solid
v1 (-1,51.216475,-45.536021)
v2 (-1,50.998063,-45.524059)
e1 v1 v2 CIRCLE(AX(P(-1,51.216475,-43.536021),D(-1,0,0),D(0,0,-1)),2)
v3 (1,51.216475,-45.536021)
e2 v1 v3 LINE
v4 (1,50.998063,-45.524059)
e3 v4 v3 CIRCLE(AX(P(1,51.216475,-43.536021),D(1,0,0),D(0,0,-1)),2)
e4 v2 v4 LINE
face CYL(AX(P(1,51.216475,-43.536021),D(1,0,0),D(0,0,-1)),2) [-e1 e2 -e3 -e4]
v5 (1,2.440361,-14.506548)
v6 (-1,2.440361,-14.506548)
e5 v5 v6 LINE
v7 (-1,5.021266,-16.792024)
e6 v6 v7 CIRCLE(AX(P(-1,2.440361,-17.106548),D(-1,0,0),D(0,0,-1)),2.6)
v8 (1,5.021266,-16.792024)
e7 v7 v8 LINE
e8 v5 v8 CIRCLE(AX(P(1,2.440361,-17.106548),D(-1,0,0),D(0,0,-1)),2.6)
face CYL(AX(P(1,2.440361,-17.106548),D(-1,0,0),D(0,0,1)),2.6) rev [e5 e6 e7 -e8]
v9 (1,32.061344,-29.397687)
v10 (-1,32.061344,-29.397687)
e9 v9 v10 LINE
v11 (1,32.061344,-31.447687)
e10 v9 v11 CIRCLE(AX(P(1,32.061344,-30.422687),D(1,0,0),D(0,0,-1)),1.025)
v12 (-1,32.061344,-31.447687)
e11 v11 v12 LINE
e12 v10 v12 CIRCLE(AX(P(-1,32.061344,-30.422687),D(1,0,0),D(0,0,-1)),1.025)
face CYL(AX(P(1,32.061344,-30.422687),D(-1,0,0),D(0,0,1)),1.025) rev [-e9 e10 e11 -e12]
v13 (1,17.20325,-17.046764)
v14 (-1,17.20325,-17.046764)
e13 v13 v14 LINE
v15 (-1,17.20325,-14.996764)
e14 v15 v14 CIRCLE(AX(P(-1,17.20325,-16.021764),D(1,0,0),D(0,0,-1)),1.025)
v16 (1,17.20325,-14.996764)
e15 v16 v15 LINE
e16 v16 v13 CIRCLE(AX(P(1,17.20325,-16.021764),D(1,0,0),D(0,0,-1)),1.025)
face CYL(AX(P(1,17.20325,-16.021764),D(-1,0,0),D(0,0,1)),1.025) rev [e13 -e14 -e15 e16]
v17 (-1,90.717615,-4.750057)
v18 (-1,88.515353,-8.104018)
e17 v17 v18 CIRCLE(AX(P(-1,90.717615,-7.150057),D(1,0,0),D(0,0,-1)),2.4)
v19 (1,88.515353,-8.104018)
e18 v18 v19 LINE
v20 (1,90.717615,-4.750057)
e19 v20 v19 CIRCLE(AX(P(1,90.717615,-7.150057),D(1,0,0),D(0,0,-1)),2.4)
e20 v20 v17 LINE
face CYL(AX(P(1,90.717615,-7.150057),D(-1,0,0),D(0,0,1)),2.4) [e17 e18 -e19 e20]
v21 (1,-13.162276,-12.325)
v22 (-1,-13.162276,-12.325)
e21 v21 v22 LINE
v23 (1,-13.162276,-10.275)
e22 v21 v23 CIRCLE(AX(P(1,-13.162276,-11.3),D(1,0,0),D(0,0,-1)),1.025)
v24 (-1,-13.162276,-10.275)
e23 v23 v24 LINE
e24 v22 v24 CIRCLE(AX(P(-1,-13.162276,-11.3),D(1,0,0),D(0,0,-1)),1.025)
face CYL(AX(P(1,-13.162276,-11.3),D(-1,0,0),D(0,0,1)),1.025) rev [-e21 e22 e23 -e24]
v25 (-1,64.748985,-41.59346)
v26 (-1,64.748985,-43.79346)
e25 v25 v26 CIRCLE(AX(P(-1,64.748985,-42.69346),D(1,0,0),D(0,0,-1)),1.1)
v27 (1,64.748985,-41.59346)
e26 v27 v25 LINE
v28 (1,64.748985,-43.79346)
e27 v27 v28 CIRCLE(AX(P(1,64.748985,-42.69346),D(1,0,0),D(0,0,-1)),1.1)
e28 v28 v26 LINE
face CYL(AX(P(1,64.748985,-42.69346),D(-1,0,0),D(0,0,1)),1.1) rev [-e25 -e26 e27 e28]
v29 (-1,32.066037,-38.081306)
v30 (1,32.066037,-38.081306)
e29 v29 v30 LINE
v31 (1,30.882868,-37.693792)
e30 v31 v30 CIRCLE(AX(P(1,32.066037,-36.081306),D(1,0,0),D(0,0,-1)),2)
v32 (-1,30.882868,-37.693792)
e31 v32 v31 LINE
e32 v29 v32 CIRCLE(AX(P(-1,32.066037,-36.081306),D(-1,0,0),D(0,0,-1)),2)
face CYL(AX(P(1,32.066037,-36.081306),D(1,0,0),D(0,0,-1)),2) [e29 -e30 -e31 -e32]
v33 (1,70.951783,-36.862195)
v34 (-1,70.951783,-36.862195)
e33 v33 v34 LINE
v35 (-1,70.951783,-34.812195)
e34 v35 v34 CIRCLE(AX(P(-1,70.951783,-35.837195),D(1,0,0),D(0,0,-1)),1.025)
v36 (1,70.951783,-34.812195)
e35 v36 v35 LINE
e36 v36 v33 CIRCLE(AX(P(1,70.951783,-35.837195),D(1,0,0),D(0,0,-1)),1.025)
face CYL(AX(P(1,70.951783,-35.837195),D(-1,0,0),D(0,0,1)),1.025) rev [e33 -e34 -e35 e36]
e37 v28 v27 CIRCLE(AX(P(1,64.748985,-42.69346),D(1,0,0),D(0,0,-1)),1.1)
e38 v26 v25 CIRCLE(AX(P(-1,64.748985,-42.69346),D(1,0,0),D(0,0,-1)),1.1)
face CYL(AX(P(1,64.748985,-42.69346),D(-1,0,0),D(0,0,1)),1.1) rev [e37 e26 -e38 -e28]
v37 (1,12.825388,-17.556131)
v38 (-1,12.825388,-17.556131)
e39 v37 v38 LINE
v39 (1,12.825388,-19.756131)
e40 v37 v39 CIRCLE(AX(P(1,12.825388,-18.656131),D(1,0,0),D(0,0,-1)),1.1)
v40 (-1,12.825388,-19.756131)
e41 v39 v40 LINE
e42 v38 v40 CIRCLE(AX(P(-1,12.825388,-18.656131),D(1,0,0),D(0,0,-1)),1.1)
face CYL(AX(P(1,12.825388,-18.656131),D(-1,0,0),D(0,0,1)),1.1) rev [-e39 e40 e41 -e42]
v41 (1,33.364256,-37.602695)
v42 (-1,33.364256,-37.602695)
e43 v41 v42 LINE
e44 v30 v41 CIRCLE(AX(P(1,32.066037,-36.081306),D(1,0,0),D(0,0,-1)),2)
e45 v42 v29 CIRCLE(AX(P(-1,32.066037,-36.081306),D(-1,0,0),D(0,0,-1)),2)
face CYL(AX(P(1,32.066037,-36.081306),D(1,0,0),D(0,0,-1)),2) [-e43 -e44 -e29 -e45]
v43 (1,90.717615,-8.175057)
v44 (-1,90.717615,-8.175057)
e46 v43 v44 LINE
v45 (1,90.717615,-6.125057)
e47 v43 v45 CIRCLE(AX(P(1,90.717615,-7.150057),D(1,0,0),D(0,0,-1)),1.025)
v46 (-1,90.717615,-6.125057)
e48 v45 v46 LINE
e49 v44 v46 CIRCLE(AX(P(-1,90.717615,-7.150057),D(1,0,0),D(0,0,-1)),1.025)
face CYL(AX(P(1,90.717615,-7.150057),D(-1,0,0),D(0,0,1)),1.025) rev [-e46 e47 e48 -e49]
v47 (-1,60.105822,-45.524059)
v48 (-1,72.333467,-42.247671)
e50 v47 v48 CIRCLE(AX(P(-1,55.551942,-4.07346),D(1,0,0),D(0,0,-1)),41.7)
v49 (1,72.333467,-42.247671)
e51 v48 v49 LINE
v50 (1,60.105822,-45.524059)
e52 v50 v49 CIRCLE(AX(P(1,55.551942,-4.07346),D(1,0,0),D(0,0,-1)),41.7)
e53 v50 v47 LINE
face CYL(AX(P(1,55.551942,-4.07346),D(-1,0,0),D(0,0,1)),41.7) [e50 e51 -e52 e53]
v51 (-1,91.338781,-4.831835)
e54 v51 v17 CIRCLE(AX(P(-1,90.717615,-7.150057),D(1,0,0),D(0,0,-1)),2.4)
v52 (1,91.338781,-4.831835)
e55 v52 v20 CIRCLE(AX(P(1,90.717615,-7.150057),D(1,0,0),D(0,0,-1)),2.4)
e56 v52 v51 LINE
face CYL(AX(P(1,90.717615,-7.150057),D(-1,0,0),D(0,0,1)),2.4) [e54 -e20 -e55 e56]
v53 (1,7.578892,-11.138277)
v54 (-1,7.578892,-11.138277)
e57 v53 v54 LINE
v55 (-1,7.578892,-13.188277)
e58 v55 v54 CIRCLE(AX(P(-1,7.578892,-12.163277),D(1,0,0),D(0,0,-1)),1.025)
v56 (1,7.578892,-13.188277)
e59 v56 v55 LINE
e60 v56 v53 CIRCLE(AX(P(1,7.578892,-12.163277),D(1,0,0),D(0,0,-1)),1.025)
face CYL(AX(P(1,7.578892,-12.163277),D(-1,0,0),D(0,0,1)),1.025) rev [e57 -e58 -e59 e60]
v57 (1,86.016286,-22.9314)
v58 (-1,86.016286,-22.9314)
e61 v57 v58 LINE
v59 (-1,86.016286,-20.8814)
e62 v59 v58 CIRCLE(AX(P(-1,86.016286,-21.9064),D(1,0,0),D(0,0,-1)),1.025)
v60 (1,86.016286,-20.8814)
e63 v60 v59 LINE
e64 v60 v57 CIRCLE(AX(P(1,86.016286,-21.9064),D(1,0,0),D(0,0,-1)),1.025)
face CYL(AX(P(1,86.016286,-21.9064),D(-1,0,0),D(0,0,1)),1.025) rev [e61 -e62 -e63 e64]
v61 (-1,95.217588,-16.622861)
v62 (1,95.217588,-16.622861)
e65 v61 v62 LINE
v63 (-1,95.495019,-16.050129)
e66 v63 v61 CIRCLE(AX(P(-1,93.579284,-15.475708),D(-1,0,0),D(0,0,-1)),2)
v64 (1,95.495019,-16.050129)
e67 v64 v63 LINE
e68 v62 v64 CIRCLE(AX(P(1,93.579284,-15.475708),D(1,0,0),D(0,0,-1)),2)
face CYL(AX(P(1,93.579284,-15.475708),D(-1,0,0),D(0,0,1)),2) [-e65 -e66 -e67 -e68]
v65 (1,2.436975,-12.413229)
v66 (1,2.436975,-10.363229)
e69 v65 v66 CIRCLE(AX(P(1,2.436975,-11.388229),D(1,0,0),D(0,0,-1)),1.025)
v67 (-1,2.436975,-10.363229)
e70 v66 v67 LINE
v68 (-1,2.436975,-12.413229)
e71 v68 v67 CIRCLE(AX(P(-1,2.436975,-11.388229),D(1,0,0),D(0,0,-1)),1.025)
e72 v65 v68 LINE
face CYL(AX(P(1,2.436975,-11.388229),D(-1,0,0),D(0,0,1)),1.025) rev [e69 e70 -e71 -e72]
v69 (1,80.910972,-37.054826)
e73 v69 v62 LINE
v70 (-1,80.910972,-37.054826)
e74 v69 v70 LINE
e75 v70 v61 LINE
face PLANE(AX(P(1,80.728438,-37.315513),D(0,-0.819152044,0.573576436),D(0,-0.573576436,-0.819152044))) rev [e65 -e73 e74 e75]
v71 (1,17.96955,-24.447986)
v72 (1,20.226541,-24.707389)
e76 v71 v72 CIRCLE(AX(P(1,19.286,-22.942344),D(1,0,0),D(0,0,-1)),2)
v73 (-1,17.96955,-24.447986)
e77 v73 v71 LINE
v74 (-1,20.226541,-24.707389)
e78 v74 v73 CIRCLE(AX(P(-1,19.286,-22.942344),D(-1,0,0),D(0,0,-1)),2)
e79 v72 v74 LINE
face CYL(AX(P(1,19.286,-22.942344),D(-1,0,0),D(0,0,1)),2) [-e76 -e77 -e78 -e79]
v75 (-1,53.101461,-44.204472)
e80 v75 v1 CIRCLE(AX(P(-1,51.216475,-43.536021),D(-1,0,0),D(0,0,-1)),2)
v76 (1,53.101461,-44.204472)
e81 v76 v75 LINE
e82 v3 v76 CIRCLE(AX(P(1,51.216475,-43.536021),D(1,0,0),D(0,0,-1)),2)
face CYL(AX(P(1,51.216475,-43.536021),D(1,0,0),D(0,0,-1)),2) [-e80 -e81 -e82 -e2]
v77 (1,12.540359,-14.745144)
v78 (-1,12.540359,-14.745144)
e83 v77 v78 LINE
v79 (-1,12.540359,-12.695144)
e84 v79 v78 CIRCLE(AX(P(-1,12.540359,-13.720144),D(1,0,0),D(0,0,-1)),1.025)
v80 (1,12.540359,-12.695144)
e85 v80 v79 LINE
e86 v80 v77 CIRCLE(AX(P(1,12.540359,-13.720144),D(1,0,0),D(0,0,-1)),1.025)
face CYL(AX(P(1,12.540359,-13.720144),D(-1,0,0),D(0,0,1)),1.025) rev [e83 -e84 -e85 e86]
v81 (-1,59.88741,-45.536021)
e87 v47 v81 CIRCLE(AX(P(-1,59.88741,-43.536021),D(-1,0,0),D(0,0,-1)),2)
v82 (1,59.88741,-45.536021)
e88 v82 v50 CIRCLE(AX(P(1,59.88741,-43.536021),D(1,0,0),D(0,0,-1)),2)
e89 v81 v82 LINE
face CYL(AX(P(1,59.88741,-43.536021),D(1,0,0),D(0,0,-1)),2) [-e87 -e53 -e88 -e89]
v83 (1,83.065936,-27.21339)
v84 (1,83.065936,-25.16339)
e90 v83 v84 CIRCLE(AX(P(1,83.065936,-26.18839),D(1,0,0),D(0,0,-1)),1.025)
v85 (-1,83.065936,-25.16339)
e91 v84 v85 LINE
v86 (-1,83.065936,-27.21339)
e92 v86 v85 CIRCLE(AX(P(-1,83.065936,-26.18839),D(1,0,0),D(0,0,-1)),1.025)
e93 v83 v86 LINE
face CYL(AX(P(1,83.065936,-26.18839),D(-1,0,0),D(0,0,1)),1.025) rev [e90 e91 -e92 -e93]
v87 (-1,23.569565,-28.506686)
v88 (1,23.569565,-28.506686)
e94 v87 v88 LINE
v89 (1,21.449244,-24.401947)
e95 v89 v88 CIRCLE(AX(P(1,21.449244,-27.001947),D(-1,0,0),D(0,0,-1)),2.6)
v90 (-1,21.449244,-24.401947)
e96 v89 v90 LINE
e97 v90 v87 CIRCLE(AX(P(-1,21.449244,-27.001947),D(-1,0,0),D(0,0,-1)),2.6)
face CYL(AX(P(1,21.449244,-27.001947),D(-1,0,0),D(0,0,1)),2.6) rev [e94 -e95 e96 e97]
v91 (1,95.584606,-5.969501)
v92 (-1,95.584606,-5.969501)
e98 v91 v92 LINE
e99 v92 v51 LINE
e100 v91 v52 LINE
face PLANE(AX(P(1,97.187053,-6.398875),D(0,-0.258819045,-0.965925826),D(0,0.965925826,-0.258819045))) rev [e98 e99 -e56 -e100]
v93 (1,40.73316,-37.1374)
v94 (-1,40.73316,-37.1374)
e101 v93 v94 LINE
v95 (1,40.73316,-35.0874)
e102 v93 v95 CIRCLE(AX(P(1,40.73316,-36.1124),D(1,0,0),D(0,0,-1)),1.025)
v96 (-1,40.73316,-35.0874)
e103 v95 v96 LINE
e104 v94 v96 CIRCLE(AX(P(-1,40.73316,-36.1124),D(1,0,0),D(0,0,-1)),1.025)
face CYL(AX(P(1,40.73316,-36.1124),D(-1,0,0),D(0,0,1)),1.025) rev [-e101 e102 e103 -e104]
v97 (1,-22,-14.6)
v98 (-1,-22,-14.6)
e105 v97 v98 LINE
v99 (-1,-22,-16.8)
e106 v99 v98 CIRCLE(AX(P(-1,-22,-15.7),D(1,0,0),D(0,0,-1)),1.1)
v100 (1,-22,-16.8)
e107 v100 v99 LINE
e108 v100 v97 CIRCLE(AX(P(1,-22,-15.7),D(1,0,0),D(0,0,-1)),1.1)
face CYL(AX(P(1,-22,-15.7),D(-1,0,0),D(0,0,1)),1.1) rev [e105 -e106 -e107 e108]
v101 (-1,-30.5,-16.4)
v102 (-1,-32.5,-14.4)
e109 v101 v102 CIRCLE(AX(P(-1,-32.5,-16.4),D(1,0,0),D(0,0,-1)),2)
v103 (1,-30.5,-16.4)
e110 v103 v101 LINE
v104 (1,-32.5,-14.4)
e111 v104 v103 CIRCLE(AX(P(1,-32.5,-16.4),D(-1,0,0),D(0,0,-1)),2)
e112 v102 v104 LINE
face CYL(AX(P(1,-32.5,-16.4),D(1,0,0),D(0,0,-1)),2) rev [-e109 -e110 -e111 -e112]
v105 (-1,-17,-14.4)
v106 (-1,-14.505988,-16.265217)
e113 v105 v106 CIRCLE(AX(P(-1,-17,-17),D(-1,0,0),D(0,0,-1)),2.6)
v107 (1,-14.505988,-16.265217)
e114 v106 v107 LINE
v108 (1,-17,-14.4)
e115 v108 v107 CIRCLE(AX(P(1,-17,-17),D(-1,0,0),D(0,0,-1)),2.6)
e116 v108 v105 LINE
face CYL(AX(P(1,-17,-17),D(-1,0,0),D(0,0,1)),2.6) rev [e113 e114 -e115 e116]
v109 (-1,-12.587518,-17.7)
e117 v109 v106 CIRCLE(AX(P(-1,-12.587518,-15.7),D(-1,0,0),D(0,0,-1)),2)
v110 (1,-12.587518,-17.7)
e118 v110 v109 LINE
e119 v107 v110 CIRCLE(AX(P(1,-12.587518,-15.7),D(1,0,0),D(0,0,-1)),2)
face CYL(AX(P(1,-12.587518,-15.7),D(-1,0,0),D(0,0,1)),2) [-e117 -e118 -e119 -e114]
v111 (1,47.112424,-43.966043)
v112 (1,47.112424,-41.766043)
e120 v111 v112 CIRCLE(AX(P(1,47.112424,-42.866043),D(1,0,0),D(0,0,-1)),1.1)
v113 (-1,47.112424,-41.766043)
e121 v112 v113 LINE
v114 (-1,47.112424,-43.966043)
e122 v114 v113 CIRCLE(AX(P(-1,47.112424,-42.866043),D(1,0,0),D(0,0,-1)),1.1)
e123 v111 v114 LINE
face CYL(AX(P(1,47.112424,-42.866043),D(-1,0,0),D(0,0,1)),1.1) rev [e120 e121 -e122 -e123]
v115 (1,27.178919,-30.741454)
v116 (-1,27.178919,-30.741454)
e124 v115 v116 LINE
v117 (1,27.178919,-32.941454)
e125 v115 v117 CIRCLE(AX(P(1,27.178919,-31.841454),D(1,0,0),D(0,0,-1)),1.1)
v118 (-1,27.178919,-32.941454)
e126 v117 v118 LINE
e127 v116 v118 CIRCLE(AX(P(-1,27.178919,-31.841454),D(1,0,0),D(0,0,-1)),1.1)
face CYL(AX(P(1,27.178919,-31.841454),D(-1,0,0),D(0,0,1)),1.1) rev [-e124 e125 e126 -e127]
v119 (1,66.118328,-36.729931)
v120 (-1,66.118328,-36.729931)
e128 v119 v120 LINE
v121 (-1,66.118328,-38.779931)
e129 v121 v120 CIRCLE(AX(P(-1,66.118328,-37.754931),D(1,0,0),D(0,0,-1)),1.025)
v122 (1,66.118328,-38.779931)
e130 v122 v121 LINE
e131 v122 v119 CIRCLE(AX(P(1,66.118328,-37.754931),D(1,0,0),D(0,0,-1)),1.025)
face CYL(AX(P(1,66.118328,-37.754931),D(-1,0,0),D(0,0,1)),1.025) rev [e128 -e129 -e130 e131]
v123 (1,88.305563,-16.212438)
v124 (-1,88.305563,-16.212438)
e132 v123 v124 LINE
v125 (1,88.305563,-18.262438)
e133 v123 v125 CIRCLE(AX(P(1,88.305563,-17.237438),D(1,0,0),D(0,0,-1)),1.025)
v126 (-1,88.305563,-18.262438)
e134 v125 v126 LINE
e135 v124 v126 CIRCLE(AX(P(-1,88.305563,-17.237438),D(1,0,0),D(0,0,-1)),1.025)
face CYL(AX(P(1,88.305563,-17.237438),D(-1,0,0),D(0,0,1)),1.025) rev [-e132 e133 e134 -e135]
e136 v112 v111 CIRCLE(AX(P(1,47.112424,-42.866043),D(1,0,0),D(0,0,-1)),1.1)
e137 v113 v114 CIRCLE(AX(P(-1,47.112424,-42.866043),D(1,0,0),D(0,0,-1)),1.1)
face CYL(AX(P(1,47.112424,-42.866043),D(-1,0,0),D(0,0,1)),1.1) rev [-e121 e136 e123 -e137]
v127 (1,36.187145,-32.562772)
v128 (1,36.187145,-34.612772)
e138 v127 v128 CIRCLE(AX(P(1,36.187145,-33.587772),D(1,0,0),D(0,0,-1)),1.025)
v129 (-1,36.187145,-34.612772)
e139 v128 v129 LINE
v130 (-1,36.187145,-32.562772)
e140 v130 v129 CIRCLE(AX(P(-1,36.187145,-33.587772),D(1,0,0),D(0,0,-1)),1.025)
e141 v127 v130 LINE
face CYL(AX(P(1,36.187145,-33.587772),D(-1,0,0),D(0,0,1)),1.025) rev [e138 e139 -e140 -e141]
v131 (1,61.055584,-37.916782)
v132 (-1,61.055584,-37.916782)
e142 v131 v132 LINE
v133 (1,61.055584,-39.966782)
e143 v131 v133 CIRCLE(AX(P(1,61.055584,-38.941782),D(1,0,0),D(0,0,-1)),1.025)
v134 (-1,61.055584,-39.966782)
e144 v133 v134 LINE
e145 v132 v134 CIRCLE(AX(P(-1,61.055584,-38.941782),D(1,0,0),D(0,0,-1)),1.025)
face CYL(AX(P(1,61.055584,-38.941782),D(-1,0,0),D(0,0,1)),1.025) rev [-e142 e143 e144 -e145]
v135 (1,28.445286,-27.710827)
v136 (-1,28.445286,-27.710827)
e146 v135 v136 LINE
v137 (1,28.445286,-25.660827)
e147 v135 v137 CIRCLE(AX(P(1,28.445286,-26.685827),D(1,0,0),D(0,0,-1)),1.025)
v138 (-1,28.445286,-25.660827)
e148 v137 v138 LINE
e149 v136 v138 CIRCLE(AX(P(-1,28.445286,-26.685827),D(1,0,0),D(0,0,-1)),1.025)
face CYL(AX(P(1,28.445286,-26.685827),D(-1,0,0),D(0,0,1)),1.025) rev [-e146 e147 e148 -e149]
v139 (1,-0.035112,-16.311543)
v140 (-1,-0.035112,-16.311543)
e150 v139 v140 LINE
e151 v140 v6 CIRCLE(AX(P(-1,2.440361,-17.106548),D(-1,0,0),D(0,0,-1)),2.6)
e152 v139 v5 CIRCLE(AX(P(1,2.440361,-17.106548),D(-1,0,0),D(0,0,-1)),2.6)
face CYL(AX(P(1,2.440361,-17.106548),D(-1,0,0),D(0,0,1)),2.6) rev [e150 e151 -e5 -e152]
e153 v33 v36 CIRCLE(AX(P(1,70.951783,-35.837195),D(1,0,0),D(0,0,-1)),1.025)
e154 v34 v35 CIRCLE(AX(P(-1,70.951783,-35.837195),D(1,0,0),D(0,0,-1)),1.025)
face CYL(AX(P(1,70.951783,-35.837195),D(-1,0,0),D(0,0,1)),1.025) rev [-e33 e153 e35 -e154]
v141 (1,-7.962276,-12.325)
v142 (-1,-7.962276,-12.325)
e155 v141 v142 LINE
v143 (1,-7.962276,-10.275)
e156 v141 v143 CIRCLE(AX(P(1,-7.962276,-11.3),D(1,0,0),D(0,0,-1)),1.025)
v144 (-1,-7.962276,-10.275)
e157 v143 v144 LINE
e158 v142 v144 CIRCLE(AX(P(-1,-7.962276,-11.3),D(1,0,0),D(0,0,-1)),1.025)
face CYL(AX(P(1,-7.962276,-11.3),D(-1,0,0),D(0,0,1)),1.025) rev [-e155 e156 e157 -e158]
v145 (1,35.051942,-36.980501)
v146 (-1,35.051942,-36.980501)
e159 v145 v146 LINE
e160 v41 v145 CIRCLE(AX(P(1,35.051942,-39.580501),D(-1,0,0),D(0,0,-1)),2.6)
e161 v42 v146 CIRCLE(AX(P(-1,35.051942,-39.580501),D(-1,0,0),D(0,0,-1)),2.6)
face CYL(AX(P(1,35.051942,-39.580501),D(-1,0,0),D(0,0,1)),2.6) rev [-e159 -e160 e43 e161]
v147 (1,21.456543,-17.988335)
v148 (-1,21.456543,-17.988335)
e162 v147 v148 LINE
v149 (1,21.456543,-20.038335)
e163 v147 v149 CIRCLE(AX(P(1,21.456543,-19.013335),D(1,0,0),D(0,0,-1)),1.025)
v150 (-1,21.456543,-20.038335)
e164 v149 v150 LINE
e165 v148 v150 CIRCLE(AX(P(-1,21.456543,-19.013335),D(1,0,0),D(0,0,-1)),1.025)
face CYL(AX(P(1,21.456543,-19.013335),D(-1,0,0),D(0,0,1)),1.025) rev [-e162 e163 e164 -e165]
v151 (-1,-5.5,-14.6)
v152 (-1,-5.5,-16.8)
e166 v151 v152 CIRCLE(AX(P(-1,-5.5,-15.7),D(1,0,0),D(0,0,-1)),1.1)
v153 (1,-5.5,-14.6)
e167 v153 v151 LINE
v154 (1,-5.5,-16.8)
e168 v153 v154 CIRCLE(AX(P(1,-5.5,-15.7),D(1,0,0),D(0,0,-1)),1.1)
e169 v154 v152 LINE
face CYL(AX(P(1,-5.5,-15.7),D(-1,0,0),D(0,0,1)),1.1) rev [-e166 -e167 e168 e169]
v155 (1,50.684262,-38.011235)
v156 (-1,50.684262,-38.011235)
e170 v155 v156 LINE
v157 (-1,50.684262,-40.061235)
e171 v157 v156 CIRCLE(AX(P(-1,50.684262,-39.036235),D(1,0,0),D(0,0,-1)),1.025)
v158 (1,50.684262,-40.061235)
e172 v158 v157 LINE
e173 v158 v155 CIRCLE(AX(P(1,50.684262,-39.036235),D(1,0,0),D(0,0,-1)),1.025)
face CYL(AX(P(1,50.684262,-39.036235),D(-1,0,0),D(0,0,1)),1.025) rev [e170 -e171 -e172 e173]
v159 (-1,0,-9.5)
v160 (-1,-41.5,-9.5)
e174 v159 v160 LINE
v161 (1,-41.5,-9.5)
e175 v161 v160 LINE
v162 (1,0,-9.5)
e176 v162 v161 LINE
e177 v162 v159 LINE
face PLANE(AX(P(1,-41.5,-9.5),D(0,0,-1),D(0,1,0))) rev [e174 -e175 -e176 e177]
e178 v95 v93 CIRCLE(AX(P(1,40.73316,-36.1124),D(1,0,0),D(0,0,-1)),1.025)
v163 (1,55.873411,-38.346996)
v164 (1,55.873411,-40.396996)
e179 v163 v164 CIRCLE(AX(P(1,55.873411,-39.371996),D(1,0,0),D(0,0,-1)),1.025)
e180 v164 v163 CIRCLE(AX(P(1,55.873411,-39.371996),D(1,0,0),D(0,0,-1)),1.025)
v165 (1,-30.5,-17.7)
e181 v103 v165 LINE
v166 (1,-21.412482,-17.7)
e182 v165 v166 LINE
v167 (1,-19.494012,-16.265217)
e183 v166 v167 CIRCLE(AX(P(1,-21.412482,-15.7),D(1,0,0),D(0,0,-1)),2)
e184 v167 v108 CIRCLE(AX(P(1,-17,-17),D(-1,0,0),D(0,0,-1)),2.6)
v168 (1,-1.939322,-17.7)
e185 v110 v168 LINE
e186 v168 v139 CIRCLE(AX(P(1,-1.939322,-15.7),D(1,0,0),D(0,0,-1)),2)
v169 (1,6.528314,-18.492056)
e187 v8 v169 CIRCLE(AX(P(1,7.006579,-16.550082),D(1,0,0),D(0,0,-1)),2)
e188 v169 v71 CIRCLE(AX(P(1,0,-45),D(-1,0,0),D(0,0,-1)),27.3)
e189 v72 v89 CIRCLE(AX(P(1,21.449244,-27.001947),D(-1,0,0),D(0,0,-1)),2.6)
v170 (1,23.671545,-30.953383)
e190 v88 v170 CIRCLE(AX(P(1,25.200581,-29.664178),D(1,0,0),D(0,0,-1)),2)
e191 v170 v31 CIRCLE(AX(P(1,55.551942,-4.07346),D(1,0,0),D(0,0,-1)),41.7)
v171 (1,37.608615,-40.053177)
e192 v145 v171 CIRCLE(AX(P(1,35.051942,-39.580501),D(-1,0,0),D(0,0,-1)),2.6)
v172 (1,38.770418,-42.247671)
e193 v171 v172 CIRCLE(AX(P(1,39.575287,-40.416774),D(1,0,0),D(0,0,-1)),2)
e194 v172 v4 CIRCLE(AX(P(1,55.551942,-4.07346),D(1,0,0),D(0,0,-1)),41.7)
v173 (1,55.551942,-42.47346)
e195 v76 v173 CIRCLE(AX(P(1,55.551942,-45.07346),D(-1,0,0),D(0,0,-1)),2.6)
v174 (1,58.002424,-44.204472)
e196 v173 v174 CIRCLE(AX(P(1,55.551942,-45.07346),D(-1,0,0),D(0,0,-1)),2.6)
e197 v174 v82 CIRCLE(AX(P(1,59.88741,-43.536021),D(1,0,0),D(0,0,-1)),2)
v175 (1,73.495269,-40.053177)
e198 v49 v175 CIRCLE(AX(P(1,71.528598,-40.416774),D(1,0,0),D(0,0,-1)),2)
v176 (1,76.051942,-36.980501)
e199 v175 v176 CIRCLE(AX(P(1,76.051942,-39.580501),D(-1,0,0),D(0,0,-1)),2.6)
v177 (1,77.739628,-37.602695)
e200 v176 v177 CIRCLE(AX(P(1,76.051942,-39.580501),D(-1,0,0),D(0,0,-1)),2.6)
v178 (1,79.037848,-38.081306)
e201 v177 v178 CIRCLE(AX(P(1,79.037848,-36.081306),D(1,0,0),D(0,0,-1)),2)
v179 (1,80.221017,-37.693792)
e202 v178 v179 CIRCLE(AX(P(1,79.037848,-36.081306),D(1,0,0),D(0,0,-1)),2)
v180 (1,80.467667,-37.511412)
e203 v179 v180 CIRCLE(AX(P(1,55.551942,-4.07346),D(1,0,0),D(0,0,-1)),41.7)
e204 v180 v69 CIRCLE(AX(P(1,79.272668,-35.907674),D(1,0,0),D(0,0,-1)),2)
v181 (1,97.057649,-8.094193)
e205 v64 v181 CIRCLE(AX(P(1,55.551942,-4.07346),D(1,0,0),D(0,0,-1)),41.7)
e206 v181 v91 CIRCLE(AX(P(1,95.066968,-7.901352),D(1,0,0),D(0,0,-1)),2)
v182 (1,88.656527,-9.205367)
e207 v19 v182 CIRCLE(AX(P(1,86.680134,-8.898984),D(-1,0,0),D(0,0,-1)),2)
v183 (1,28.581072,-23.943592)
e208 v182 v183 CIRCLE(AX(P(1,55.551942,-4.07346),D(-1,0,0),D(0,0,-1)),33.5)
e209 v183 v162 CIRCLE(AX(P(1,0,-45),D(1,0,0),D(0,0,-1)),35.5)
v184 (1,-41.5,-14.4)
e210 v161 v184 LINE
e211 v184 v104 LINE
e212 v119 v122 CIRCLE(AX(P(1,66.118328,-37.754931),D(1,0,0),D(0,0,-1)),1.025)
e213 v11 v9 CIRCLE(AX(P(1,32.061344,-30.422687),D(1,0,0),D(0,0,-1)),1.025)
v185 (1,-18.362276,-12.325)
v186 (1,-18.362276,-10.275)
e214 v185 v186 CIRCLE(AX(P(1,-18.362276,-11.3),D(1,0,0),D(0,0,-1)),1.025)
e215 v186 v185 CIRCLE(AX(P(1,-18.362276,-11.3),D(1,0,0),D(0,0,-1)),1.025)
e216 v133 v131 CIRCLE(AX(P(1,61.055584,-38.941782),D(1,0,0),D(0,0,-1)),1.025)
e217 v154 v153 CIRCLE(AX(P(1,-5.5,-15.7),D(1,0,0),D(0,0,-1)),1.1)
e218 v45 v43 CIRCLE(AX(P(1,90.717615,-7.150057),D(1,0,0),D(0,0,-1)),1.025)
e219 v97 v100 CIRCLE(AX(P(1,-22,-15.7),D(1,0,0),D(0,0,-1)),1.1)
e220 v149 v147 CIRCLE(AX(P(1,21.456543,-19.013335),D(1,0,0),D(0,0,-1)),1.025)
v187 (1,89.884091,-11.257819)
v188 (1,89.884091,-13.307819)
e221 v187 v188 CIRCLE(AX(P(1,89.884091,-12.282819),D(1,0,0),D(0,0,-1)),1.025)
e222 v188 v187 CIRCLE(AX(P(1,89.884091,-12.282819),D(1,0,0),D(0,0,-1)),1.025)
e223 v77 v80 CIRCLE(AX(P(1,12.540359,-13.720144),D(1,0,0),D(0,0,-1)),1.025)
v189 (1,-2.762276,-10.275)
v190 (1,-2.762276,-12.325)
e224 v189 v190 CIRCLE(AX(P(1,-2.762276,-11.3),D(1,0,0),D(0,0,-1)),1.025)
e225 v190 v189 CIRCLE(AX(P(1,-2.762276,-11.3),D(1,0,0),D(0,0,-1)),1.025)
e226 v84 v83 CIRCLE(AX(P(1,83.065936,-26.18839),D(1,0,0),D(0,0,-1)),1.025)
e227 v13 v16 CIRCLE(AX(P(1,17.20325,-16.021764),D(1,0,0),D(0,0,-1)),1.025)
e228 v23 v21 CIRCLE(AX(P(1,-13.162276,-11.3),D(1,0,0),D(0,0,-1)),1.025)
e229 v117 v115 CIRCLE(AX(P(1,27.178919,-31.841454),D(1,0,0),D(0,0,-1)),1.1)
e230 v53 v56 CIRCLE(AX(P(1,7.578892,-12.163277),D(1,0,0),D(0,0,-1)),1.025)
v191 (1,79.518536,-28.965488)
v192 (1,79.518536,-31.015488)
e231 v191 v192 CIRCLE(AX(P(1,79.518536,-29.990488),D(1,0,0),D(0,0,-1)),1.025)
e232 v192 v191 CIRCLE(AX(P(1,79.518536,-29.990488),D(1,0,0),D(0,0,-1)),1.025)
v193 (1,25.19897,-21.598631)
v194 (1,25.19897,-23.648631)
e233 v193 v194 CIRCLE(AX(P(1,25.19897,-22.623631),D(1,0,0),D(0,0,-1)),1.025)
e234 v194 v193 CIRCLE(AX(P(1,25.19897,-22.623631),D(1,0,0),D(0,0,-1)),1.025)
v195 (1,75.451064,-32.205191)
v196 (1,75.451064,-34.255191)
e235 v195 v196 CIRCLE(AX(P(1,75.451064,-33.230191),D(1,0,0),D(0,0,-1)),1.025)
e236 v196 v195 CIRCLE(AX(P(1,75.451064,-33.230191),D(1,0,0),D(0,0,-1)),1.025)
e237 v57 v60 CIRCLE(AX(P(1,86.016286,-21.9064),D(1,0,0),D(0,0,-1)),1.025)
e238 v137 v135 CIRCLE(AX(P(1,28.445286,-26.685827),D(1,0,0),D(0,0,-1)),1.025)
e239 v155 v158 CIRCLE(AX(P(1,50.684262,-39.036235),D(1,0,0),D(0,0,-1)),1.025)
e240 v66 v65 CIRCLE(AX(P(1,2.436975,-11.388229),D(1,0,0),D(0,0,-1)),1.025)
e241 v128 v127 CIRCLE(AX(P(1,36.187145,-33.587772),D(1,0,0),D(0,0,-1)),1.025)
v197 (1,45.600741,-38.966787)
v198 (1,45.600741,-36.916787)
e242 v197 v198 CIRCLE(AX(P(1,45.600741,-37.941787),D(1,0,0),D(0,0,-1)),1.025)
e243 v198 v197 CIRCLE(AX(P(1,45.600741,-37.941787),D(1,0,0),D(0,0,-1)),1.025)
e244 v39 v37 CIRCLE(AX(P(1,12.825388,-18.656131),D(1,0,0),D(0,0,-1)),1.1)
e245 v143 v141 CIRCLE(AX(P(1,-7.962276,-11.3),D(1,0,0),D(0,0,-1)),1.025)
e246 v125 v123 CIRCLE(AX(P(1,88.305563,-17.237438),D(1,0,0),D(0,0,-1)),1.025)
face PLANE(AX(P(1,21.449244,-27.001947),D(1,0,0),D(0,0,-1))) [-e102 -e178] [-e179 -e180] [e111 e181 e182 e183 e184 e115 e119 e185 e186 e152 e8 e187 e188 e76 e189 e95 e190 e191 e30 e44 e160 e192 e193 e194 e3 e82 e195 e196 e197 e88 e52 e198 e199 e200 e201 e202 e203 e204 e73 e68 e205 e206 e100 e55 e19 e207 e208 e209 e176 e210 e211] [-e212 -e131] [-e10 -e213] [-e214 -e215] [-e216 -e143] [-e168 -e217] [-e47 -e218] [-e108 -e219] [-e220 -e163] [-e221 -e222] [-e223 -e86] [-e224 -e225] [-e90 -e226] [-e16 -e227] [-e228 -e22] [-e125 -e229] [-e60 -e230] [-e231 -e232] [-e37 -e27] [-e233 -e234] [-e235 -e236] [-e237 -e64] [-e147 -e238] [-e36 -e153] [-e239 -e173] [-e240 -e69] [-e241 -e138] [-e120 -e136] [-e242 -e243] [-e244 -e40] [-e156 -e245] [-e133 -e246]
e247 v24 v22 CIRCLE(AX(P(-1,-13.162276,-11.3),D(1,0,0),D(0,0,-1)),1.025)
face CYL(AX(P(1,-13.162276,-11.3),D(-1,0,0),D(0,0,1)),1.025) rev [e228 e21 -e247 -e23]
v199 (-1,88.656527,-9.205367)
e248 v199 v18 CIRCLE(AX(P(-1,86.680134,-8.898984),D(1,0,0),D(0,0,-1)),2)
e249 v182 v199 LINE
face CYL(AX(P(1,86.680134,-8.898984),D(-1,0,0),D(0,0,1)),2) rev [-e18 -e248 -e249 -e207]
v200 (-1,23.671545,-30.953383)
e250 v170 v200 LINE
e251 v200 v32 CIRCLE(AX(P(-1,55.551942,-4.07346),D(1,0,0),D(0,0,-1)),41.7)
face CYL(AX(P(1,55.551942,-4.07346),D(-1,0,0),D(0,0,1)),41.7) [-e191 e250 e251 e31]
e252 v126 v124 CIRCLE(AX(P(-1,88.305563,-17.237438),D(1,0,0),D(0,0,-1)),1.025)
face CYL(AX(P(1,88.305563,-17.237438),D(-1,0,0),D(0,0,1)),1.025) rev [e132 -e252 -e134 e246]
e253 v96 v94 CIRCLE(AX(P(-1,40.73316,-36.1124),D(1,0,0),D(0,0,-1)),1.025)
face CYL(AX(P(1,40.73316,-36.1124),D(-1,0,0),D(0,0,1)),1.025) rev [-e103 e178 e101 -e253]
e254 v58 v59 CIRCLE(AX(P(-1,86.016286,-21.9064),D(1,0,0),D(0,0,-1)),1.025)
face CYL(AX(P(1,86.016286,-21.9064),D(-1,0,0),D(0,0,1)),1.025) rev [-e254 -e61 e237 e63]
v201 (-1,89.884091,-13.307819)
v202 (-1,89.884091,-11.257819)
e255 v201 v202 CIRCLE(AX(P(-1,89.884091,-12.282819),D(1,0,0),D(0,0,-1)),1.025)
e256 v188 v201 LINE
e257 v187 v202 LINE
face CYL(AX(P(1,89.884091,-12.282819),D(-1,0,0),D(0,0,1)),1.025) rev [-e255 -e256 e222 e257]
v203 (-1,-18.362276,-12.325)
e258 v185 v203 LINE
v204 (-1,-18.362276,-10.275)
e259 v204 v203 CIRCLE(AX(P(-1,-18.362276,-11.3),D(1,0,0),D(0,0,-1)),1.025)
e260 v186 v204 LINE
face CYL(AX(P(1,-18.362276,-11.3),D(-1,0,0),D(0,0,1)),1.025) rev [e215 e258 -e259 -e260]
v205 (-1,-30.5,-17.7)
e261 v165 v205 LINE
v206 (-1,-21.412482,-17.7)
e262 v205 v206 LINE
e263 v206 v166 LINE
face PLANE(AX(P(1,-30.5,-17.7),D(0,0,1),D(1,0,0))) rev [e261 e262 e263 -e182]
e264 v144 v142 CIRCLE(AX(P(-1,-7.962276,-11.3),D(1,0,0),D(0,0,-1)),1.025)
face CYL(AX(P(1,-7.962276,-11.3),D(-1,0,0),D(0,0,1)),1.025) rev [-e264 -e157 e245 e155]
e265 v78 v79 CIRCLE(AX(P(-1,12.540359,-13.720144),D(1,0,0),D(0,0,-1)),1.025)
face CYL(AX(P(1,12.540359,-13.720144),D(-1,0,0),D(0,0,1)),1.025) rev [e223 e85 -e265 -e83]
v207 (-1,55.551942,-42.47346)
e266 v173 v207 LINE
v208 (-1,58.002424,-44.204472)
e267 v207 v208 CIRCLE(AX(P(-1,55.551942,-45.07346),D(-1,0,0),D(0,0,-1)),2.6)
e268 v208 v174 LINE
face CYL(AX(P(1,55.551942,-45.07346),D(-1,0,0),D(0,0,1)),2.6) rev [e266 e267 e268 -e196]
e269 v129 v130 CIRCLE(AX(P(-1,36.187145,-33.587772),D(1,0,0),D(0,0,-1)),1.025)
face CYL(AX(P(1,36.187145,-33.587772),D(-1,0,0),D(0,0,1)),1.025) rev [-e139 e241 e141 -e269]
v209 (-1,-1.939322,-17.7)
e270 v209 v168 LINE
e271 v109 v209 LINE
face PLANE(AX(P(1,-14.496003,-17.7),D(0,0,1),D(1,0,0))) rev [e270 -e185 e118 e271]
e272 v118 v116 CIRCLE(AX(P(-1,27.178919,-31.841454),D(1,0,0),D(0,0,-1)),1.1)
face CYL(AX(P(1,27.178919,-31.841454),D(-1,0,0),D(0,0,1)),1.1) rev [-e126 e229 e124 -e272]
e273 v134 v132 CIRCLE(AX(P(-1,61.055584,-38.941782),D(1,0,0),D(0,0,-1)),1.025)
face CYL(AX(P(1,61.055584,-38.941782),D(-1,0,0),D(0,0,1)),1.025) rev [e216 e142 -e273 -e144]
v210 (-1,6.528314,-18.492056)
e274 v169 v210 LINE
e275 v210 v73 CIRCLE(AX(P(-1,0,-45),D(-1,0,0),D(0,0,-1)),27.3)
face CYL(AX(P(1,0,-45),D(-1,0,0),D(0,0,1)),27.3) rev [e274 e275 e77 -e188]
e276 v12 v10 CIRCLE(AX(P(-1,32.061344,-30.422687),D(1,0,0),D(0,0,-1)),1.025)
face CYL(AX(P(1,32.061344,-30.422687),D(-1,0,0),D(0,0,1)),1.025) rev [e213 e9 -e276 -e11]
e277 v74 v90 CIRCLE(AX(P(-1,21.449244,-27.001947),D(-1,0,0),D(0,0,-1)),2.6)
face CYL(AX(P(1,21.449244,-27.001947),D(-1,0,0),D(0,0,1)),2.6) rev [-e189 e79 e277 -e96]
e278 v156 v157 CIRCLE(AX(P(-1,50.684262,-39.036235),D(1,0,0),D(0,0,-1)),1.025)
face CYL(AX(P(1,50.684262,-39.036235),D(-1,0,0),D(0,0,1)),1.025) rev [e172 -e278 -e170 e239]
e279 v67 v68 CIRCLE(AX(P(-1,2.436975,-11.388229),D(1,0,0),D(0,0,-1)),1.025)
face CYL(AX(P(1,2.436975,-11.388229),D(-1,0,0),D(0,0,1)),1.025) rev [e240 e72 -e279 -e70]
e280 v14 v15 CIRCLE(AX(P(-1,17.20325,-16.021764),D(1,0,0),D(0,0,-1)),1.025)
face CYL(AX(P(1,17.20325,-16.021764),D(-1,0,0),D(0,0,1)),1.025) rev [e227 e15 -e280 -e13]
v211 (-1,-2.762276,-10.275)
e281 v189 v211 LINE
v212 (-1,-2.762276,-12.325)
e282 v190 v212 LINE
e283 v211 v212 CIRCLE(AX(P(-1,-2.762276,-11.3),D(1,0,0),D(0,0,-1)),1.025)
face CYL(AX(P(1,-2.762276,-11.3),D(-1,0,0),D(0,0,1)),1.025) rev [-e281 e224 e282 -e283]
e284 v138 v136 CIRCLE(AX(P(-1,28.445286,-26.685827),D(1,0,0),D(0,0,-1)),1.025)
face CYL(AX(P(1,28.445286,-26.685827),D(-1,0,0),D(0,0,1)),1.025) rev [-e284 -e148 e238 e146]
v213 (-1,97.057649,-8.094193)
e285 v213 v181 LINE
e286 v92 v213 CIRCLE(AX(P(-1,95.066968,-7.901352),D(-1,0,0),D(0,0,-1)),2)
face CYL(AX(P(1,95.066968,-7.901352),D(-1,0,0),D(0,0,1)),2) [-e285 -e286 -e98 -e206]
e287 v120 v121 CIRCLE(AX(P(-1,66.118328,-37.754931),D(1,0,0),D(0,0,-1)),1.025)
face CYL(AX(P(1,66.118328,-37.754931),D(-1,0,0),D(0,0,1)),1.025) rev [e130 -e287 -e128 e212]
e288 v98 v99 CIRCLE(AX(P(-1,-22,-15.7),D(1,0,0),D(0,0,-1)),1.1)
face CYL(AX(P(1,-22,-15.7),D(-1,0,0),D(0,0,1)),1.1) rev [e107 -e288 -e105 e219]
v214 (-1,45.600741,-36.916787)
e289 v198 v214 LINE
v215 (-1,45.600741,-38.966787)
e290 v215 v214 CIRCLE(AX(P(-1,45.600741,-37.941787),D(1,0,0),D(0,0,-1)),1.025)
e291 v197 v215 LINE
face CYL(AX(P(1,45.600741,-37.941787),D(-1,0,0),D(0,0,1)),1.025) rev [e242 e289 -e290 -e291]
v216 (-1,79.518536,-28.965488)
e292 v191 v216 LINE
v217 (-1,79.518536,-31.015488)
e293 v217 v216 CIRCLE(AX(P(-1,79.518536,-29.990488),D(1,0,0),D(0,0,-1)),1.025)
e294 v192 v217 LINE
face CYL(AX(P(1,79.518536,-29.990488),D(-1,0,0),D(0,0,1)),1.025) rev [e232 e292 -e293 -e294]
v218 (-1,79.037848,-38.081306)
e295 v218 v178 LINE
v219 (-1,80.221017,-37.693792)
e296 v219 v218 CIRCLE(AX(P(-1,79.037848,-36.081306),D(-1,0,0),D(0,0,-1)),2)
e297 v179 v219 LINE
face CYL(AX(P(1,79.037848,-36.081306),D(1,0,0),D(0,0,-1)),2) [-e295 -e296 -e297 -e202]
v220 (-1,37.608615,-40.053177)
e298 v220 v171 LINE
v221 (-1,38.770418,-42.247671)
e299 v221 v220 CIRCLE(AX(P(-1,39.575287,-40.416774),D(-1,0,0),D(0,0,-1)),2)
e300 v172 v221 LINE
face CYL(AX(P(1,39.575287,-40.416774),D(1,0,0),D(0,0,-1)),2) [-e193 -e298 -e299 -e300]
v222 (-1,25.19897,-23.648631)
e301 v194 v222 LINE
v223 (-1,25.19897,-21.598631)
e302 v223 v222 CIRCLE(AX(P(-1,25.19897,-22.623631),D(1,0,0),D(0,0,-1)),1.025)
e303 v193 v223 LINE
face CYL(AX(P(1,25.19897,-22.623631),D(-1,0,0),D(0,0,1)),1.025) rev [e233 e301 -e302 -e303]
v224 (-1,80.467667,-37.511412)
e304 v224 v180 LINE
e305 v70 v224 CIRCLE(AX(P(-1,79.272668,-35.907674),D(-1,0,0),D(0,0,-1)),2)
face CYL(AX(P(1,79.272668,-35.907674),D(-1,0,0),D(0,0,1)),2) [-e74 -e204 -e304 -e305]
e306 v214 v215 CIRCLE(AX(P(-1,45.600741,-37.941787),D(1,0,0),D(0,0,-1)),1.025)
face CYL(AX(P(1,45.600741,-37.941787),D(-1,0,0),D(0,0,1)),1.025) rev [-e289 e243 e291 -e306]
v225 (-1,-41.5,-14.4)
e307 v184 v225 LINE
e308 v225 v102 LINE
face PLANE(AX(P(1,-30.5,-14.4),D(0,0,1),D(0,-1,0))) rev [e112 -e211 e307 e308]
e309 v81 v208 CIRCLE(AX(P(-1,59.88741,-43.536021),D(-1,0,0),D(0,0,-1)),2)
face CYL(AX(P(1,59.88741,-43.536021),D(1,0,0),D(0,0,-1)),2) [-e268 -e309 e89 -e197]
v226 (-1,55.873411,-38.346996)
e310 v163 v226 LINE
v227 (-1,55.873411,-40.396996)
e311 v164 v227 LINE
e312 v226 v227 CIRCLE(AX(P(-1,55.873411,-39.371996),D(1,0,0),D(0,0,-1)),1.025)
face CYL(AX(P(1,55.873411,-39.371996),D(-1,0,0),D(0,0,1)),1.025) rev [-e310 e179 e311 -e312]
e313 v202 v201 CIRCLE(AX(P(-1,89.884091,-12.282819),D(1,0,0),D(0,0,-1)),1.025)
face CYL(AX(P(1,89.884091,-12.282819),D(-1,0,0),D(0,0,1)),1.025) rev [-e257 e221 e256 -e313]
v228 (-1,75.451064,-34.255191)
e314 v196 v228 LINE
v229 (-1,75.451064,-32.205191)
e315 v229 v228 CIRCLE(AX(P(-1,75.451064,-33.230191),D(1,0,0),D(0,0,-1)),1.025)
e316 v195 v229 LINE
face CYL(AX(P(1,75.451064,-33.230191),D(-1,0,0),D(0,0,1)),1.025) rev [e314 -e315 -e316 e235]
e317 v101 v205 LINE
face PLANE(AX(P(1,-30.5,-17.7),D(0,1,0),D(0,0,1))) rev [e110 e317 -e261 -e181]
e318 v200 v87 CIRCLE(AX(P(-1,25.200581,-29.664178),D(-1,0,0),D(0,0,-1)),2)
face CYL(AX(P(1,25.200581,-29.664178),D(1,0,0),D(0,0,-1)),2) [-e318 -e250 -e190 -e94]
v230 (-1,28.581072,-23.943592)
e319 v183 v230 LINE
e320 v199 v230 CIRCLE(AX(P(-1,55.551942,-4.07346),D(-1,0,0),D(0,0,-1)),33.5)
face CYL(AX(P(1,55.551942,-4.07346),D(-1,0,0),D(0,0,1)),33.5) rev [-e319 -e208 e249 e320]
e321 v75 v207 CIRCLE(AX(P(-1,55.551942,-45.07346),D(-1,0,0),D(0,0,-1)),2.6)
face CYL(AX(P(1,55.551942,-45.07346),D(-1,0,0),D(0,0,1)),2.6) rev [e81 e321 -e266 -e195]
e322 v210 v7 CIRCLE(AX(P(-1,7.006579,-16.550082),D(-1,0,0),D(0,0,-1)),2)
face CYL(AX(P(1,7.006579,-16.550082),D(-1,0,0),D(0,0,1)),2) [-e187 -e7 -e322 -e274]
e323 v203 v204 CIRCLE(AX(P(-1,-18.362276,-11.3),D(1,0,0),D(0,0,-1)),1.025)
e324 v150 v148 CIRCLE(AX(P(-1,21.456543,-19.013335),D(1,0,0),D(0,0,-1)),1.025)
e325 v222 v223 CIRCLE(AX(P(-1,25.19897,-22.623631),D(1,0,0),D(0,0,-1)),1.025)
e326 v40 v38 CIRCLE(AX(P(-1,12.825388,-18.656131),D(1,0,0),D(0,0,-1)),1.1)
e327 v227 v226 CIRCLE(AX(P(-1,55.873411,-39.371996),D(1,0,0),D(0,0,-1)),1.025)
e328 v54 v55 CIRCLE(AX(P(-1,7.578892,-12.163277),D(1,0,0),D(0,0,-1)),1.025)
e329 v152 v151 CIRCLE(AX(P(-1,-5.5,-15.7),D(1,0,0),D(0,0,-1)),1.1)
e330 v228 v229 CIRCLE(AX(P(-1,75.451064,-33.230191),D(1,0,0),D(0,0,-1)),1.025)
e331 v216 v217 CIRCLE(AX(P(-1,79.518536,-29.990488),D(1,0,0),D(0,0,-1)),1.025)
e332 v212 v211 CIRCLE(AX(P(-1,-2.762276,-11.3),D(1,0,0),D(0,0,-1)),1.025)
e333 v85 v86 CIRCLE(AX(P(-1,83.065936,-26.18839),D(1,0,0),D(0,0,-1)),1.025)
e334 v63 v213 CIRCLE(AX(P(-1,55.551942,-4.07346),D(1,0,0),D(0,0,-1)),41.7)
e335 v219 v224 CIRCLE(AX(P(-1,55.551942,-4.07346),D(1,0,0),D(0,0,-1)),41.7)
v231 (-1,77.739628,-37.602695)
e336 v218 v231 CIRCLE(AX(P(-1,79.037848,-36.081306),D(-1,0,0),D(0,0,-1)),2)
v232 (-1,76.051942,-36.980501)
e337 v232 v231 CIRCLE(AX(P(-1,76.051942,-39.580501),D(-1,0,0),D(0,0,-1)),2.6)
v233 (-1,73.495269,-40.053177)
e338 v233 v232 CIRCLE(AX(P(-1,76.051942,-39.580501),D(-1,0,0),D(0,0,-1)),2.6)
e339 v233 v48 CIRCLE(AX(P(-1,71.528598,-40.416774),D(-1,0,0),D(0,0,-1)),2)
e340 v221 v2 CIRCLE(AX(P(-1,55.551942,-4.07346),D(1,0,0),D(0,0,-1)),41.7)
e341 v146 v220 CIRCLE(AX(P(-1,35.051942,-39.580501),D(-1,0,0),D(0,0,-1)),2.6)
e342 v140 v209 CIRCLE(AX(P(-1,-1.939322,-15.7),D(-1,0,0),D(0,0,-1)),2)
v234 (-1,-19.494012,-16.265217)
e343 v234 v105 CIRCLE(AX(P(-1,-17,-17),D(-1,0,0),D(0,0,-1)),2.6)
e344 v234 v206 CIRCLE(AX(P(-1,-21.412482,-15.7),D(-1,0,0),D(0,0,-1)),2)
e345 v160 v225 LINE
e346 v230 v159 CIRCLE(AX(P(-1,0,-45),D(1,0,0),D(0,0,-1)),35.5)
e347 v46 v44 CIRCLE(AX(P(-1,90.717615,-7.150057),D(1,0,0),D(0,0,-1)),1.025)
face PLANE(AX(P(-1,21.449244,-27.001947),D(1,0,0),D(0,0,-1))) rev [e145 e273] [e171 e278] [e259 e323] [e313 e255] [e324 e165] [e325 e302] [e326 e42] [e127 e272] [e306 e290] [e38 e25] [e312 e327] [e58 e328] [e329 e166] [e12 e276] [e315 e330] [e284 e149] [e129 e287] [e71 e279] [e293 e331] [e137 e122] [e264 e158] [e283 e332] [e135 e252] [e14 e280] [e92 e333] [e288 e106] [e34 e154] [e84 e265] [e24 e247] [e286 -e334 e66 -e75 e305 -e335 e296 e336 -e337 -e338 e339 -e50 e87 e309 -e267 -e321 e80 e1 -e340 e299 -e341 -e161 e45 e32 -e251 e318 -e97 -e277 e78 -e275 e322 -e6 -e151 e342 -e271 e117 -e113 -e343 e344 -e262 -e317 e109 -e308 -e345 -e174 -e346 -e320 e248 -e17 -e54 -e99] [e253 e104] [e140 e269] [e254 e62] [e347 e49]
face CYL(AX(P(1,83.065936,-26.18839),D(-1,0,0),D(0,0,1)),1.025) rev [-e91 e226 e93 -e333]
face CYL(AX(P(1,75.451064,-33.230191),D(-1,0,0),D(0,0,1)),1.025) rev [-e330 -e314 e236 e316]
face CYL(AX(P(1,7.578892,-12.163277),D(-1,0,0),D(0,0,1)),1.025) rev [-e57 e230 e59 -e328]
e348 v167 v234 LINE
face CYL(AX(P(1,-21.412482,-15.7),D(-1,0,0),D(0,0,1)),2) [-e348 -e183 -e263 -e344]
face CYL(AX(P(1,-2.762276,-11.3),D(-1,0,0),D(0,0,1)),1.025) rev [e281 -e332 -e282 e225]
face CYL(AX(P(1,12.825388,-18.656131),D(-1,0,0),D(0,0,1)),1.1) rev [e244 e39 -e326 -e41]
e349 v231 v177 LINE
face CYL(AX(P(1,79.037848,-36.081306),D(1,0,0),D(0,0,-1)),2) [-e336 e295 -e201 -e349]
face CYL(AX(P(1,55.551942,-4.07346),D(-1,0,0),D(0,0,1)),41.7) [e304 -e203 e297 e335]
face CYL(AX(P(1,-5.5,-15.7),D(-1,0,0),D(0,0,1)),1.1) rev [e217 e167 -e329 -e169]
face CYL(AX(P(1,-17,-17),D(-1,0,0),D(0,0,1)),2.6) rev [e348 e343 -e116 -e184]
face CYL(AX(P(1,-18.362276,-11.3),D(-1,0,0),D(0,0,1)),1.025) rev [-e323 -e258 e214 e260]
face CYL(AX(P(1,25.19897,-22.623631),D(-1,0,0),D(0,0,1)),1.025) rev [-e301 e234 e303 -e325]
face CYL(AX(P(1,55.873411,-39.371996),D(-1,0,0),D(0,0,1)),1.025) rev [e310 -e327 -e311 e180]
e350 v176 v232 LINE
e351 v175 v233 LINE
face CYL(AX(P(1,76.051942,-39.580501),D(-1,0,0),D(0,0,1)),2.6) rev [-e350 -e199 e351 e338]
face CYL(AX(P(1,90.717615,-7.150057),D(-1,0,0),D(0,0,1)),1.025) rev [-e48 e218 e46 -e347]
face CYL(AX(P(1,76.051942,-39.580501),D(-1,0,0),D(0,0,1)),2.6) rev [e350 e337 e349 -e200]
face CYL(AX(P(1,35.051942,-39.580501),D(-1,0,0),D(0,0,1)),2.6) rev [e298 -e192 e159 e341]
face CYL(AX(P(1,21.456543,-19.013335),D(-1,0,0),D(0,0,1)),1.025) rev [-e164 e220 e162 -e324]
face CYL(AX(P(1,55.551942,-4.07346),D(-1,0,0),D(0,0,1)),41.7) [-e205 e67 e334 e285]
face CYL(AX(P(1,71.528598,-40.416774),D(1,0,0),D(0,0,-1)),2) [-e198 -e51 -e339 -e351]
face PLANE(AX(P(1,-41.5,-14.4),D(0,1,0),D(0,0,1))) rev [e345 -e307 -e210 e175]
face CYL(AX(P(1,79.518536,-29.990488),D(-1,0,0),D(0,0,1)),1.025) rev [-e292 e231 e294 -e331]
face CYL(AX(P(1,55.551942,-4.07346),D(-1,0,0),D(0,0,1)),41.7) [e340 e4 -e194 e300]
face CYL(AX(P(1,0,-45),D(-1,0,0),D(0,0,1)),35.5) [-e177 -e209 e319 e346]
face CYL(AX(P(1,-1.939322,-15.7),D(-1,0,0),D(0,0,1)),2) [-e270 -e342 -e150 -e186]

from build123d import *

# Parameters (mm, degrees)
SKETCH_3_R      = 1.025
SKETCH_3_R_2    = 1.1
EXTRUDE_1_DEPTH = 1
FILLET_R2_1_R   = 2


with BuildPart() as part:
    # 草图3 → 凸台-拉伸1 (new, symmetric)
    with BuildSketch(Plane(origin=(0, 0, 0), x_dir=(0, 0, -1), z_dir=(1, 0, 0))):
        with BuildLine():
            Line((17.7, -14.496003195), (17.7, -0.091005487))
            ThreePointArc((17.7, -0.091005487), (14.516449024, 2.667043271), (18.130694373, 4.830156842))
            ThreePointArc((18.130694373, 4.830156842), (20.784604254, 12.605737141), (25.63176658, 19.239582485))
            ThreePointArc((25.63176658, 19.239582485), (25.323964311, 23.435289305), (29.409373215, 22.431231514))
            ThreePointArc((29.409373215, 22.431231514), (34.557047376, 27.097753162), (38.858437765, 32.554218527))
            ThreePointArc((38.858437765, 32.554218527), (37.328835208, 36.351942354), (41.382561796, 36.926129595))
            ThreePointArc((41.382561796, 36.926129595), (44.352566659, 44.759188173), (45.696996288, 53.027818322))
            ThreePointArc((45.696996288, 53.027818322), (42.473459702, 55.551942354), (45.696996288, 58.076066385))
            ThreePointArc((45.696996288, 58.076066385), (44.352566659, 66.344696534), (41.382561796, 74.177755113))
            ThreePointArc((41.382561796, 74.177755113), (37.328835208, 74.751942354), (38.858437765, 78.54966618))
            ThreePointArc((38.858437765, 78.54966618), (38.104416138, 79.651403013), (37.315512578, 80.728437754))
            Line((37.315512578, 80.728437754), (16.362174958, 95.400122706))
            ThreePointArc((16.362174958, 95.400122706), (11.434946284, 96.597021417), (6.398875236, 97.187053049))
            Line((6.398875236, 97.187053049), (4.831835438, 91.338780905))
            ThreePointArc((4.831835438, 91.338780905), (5.775264763, 88.750397581), (8.530219021, 88.754160598))
            ThreePointArc((8.530219021, 88.754160598), (36.525725618, 63.864609611), (23.943591586, 28.581071791))
            ThreePointArc((23.943591586, 28.581071791), (13.315993793, 16.011675448), (9.5, 0))
            Line((9.5, 0), (9.5, -41.5))
            Line((9.5, -41.5), (14.4, -41.5))
            Line((14.4, -41.5), (14.4, -30.5))
            Line((14.4, -30.5), (17.7, -30.5))
            Line((17.7, -30.5), (17.7, -19.503996805))
            ThreePointArc((17.7, -19.503996805), (14.4, -17), (17.7, -14.496003195))
        make_face()
        with Locations((11.3, -18.362276)):
            Circle(SKETCH_3_R, mode=Mode.SUBTRACT)
        with Locations((15.7, -22)):
            Circle(SKETCH_3_R_2, mode=Mode.SUBTRACT)
        with Locations((15.7, -5.5)):
            Circle(SKETCH_3_R_2, mode=Mode.SUBTRACT)
        with Locations((18.656131285, 12.825388146)):
            Circle(SKETCH_3_R_2, mode=Mode.SUBTRACT)
        with Locations((42.693459702, 64.748985357)):
            Circle(SKETCH_3_R_2, mode=Mode.SUBTRACT)
        with Locations((31.841454389, 27.178918703)):
            Circle(SKETCH_3_R_2, mode=Mode.SUBTRACT)
        with Locations((42.866043117, 47.112423882)):
            Circle(SKETCH_3_R_2, mode=Mode.SUBTRACT)
        with Locations((7.150057421, 90.717615196)):
            Circle(SKETCH_3_R, mode=Mode.SUBTRACT)
        with Locations((12.2828186, 89.884090939)):
            Circle(SKETCH_3_R, mode=Mode.SUBTRACT)
        with Locations((17.237437698, 88.305563273)):
            Circle(SKETCH_3_R, mode=Mode.SUBTRACT)
        with Locations((21.90640009, 86.016286055)):
            Circle(SKETCH_3_R, mode=Mode.SUBTRACT)
        with Locations((26.188389865, 83.065936319)):
            Circle(SKETCH_3_R, mode=Mode.SUBTRACT)
        with Locations((29.990488371, 79.518536292)):
            Circle(SKETCH_3_R, mode=Mode.SUBTRACT)
        with Locations((33.230190537, 75.451064119)):
            Circle(SKETCH_3_R, mode=Mode.SUBTRACT)
        with Locations((35.837195224, 70.951783448)):
            Circle(SKETCH_3_R, mode=Mode.SUBTRACT)
        with Locations((37.75493075, 66.118328115)):
            Circle(SKETCH_3_R, mode=Mode.SUBTRACT)
        with Locations((38.94178249, 61.055583509)):
            Circle(SKETCH_3_R, mode=Mode.SUBTRACT)
        with Locations((39.371995907, 55.873410565)):
            Circle(SKETCH_3_R, mode=Mode.SUBTRACT)
        with Locations((39.036235422, 50.684261801)):
            Circle(SKETCH_3_R, mode=Mode.SUBTRACT)
        with Locations((37.941786997, 45.600741107)):
            Circle(SKETCH_3_R, mode=Mode.SUBTRACT)
        with Locations((36.112400028, 40.733160259)):
            Circle(SKETCH_3_R, mode=Mode.SUBTRACT)
        with Locations((33.587771989, 36.187145162)):
            Circle(SKETCH_3_R, mode=Mode.SUBTRACT)
        with Locations((30.422686996, 32.061343787)):
            Circle(SKETCH_3_R, mode=Mode.SUBTRACT)
        with Locations((26.685827006, 28.445285516)):
            Circle(SKETCH_3_R, mode=Mode.SUBTRACT)
        with Locations((22.623630861, 25.1989703)):
            Circle(SKETCH_3_R, mode=Mode.SUBTRACT)
        with Locations((19.013334846, 21.456542922)):
            Circle(SKETCH_3_R, mode=Mode.SUBTRACT)
        with Locations((16.021763505, 17.203249973)):
            Circle(SKETCH_3_R, mode=Mode.SUBTRACT)
        with Locations((13.7201441, 12.54035944)):
            Circle(SKETCH_3_R, mode=Mode.SUBTRACT)
        with Locations((12.163276612, 7.57889155)):
            Circle(SKETCH_3_R, mode=Mode.SUBTRACT)
        with Locations((11.388228987, 2.43697545)):
            Circle(SKETCH_3_R, mode=Mode.SUBTRACT)
        with Locations((11.3, -2.762276)):
            Circle(SKETCH_3_R, mode=Mode.SUBTRACT)
        with Locations((11.3, -7.962276)):
            Circle(SKETCH_3_R, mode=Mode.SUBTRACT)
        with Locations((11.3, -13.162276)):
            Circle(SKETCH_3_R, mode=Mode.SUBTRACT)
    extrude(amount=EXTRUDE_1_DEPTH, both=True)

    # R2 圆角1
    fillet_r2_1_edges = [part.edges().sort_by_distance(p)[0] for p in [
        (0, 19.239582485, -25.63176658),
        (0, 4.830156842, -18.130694373),
        (0, -0.091005487, -17.7),
        (0, -14.496003195, -17.7),
        (0, -19.503996805, -17.7),
        (0, -30.5, -14.4),
        (0, 88.754160598, -8.530219021),
        (0, 97.187053049, -6.398875236),
        (0, 95.400122706, -16.362174958),
        (0, 80.728437754, -37.315512578),
        (0, 78.54966618, -38.858437765),
        (0, 74.177755113, -41.382561796),
        (0, 58.076066385, -45.696996288),
        (0, 53.027818322, -45.696996288),
        (0, 36.926129595, -41.382561796),
        (0, 32.554218527, -38.858437765),
        (0, 22.431231514, -29.409373215),
    ]]
    fillet(fillet_r2_1_edges, radius=FILLET_R2_1_R)


solid = part.part
